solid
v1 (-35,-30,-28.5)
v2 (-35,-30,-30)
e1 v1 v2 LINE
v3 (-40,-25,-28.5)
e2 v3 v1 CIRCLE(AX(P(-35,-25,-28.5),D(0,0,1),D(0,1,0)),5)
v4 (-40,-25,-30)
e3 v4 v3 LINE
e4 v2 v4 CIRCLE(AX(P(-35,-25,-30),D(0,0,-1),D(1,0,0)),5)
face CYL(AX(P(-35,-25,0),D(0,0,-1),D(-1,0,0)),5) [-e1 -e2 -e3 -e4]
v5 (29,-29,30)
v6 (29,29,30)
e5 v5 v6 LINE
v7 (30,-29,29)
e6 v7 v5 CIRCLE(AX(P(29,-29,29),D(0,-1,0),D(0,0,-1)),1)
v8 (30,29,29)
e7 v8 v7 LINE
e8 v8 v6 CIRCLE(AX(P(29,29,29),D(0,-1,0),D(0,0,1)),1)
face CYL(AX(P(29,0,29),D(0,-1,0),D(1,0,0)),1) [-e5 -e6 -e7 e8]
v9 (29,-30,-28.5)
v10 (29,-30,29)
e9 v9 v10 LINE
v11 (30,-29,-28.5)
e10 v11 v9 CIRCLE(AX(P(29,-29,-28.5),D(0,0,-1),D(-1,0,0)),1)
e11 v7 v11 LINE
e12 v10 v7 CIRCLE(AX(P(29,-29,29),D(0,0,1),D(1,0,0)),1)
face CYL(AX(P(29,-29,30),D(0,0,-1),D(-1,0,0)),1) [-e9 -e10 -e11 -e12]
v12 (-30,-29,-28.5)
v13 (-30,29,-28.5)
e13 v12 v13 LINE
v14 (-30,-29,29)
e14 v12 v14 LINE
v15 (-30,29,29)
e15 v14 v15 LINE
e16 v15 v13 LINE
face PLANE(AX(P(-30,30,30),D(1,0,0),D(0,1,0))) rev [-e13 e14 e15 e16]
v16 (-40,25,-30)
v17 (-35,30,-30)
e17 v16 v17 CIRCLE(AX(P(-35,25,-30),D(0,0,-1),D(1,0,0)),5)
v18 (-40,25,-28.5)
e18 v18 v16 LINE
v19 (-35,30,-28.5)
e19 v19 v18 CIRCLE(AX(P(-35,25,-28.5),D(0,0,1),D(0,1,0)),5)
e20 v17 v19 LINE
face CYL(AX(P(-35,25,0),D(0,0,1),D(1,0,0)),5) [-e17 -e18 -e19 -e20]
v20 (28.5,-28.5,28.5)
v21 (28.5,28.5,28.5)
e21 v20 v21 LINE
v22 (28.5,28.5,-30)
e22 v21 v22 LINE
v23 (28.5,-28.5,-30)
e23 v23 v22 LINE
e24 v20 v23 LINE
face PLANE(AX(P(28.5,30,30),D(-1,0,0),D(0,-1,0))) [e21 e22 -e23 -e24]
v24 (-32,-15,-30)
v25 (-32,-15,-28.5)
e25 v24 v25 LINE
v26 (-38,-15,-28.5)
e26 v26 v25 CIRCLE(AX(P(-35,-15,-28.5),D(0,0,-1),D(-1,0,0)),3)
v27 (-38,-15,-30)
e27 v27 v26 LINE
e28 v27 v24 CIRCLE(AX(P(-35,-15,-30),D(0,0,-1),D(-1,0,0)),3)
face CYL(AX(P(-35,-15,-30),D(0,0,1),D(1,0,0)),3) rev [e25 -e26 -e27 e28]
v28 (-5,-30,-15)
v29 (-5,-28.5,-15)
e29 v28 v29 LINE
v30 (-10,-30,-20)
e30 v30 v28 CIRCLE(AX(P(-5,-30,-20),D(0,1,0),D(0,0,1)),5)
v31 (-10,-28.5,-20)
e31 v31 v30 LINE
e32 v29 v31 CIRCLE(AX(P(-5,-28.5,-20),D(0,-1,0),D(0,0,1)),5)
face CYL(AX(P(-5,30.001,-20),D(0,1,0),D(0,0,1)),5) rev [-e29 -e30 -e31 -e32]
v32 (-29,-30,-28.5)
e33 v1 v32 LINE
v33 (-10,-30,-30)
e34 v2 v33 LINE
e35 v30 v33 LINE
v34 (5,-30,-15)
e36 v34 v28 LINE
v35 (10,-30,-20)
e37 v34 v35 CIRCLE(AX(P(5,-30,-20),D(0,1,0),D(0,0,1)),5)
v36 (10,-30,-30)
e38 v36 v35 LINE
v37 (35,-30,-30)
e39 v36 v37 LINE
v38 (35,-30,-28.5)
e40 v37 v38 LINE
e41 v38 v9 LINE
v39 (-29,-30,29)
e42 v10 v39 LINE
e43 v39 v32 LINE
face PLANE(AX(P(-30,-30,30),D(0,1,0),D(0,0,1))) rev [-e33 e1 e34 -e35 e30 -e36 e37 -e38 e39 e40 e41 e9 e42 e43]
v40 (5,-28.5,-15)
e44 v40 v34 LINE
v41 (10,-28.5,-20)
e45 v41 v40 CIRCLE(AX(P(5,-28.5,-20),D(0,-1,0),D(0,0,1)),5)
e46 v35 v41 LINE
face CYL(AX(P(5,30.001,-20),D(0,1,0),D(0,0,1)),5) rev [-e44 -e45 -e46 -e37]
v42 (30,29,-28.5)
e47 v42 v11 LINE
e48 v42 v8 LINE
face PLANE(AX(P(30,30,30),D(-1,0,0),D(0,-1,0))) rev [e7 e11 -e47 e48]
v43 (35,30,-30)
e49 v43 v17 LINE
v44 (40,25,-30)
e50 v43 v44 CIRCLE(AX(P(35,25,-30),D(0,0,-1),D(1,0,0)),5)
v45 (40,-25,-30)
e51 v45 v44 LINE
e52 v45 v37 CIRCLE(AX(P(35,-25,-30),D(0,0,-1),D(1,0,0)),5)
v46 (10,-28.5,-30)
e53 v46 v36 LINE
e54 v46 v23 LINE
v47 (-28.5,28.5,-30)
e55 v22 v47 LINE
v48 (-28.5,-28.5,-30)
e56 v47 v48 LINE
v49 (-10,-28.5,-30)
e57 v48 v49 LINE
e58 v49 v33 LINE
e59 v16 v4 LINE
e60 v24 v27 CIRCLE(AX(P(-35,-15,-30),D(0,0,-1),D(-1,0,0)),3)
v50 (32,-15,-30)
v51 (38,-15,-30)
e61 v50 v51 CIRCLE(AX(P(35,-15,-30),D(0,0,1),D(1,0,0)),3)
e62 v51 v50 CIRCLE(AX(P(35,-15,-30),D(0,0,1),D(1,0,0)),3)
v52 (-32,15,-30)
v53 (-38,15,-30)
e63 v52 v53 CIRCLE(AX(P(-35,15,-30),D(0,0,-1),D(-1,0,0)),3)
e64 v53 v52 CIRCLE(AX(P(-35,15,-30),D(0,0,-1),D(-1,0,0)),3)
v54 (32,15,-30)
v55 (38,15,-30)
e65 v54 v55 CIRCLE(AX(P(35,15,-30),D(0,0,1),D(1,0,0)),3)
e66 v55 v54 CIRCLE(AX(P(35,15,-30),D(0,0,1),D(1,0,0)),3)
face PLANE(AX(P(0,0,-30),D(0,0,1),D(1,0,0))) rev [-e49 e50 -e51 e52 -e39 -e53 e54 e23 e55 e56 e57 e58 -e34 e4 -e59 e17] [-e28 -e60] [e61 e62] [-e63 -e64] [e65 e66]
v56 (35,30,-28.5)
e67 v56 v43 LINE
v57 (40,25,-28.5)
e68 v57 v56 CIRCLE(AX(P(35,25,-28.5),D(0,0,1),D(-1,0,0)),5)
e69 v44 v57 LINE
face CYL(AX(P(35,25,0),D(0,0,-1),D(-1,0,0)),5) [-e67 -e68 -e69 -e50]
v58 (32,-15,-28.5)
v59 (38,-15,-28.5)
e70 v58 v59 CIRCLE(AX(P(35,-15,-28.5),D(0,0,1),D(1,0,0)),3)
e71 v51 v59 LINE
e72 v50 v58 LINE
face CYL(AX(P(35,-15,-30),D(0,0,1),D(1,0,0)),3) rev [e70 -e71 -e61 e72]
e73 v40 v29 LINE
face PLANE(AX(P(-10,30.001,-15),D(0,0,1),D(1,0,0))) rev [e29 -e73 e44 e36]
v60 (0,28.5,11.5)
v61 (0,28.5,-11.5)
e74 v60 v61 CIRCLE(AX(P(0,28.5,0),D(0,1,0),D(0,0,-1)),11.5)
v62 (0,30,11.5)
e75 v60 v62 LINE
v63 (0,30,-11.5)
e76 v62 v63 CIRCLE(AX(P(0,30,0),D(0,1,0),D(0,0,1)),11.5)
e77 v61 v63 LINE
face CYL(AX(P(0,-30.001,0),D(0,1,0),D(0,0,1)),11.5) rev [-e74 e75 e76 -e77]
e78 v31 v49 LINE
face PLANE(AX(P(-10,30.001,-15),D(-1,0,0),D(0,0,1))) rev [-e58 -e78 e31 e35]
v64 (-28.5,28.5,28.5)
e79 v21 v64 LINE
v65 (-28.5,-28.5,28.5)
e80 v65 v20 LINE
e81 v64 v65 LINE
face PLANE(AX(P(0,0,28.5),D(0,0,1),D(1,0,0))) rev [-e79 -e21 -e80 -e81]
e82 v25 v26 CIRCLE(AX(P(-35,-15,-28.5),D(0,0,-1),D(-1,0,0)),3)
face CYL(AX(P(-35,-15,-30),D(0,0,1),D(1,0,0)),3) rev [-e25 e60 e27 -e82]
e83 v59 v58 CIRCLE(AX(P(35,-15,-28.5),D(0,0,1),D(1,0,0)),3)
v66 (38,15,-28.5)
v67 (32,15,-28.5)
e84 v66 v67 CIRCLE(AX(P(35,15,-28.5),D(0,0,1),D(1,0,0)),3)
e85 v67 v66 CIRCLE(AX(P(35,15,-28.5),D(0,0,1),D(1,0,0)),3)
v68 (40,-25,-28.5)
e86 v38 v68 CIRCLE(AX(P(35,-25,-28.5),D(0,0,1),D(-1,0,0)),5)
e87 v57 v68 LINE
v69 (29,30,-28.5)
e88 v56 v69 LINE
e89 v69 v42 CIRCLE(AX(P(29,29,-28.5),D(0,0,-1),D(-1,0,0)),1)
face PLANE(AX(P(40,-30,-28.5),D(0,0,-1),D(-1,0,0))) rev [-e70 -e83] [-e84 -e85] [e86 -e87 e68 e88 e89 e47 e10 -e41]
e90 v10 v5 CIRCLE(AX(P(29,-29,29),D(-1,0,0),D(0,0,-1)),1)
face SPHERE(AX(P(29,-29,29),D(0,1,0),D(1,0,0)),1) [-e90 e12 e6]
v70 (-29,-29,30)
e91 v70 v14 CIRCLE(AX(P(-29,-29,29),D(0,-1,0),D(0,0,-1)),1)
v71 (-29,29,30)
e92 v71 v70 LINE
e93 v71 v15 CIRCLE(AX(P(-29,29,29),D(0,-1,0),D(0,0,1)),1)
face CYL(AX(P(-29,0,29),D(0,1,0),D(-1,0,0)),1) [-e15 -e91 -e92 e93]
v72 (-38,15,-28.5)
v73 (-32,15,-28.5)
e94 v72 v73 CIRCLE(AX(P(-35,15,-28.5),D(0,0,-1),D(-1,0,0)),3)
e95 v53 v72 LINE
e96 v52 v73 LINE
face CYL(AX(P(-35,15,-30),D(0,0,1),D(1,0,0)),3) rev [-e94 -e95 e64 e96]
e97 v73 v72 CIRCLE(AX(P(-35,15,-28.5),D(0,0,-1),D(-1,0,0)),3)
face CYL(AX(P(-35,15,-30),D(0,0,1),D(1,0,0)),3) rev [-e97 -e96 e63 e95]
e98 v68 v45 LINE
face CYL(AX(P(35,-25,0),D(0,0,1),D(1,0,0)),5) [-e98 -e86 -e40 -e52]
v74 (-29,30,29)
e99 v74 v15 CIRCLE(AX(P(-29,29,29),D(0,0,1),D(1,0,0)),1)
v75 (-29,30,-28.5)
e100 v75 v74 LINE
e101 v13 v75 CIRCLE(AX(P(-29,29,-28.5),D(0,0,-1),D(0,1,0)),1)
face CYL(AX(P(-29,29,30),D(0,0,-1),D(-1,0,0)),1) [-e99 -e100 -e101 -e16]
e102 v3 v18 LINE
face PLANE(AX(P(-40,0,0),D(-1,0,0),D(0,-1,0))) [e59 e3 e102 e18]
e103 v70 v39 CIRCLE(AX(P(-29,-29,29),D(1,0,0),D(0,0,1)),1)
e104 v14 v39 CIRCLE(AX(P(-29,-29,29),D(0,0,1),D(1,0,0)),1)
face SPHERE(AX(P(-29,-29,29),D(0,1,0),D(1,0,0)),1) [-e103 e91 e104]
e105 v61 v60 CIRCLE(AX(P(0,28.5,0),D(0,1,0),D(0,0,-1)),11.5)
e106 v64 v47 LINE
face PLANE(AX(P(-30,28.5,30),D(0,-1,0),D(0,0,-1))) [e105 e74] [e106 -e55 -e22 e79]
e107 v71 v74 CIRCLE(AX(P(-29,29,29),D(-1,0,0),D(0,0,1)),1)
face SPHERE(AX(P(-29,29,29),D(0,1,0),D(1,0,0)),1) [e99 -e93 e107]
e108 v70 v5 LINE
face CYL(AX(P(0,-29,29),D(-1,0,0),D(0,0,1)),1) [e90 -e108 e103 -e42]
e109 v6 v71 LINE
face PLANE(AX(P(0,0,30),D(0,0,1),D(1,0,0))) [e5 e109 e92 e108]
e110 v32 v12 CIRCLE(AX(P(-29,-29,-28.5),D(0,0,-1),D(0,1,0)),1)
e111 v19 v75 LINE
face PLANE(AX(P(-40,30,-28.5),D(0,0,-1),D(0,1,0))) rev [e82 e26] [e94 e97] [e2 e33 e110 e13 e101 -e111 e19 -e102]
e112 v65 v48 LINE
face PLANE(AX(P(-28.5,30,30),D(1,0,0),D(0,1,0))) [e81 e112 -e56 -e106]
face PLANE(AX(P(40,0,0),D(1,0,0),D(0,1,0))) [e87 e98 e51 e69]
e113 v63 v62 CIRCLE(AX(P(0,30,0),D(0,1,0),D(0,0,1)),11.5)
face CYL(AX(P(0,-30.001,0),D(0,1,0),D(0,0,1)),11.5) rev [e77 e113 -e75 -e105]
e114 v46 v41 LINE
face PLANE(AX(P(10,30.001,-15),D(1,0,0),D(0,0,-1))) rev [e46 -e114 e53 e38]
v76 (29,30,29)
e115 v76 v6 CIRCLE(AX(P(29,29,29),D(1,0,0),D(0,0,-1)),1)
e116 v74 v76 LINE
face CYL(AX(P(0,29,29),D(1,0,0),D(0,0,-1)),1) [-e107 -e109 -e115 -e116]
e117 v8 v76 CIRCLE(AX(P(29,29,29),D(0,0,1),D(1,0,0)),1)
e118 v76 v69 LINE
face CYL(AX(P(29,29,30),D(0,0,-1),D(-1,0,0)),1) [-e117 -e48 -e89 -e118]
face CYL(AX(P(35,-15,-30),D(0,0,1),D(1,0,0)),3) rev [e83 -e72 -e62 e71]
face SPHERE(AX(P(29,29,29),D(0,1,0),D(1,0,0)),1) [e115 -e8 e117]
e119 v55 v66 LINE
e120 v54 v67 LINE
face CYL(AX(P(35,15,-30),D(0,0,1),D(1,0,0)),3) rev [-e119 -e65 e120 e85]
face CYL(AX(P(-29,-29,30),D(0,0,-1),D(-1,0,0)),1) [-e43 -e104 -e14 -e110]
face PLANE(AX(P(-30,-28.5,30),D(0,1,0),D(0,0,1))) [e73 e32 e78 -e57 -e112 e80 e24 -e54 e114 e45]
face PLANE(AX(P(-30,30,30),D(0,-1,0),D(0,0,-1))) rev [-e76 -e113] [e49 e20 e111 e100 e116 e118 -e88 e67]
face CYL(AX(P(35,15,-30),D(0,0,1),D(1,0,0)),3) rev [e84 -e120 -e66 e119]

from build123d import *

# Parameters (mm, degrees)
SKETCH_1_W          = 60
SKETCH_1_H          = 60
EXTRUDE_1_DEPTH     = 30
SHELL_1_T           = -1.5
SKETCH_5_W          = 1.5
SKETCH_5_H          = 60
EXTRUDE_3_DEPTH     = 10
SKETCH_6_W          = 1.5
SKETCH_6_H          = 60
EXTRUDE_4_DEPTH     = 10
CUT_EXTRUDE_3_REACH = 80.102
SKETCH_7_W          = 20
SKETCH_7_H          = 15
FILLET_1_R          = 5
FILLET_2_R          = 5
CUT_EXTRUDE_4_REACH = 80.102
SKETCH_8_R          = 11.5
FILLET_3_R          = 1
SKETCH_9_R          = 3
CUT_EXTRUDE_5_DEPTH = 77.956156349


with BuildPart() as part:
    # 草图1 → 凸台-拉伸1 (new, symmetric)
    with BuildSketch(Plane.XY):
        Rectangle(SKETCH_1_W, SKETCH_1_H)
    extrude(amount=EXTRUDE_1_DEPTH, both=True)

    # 抽壳1
    shell_1_openings = [part.faces().sort_by_distance(p)[0] for p in [
        (0, 0, -30),
    ]]
    offset(amount=SHELL_1_T, openings=shell_1_openings, kind=Kind.INTERSECTION)

    # 草图5 → 凸台-拉伸3 (add)
    with BuildSketch(Plane(origin=(30, 0, 0), x_dir=(0, 0, -1), z_dir=(1, 0, 0))):
        with Locations((29.25, 0)):
            Rectangle(SKETCH_5_W, SKETCH_5_H)
    extrude(amount=EXTRUDE_3_DEPTH)

    # 草图6 → 凸台-拉伸4 (add)
    with BuildSketch(Plane.ZY.offset(30)):
        with Locations((-29.25, 0)):
            Rectangle(SKETCH_6_W, SKETCH_6_H)
    extrude(amount=EXTRUDE_4_DEPTH)

    # 草图7 → 切除-拉伸3 (cut, up to next)
    with BuildSketch(Plane.XZ.offset(30), mode=Mode.PRIVATE) as cut_extrude_3_sk1:
        with Locations((0, -22.5)):
            Rectangle(SKETCH_7_W, SKETCH_7_H)
    cut_extrude_3_tool1 = extrude(cut_extrude_3_sk1.sketch, amount=-CUT_EXTRUDE_3_REACH, mode=Mode.PRIVATE) & part.part
    add(cut_extrude_3_tool1.solids().sort_by_distance((0, -30, -22.5))[0], mode=Mode.SUBTRACT)

    # 圆角1
    fillet_1_edges = [part.edges().sort_by_distance(p)[0] for p in [
        (10, -29.25, -15),
        (-10, -29.25, -15),
    ]]
    fillet(fillet_1_edges, radius=FILLET_1_R)

    # 圆角2
    fillet_2_edges = [part.edges().sort_by_distance(p)[0] for p in [
        (40, 30, -29.25),
        (40, -30, -29.25),
        (-40, -30, -29.25),
        (-40, 30, -29.25),
    ]]
    fillet(fillet_2_edges, radius=FILLET_2_R)

    # 草图8 → 切除-拉伸4 (cut, up to next)
    with BuildSketch(Plane(origin=(0, 30, 0), x_dir=(1, 0, 0), z_dir=(0, 1, 0)), mode=Mode.PRIVATE) as cut_extrude_4_sk1:
        with Locations(Location((0, 0, 0), (0, 0, 270))):
            Circle(SKETCH_8_R)
    cut_extrude_4_tool1 = extrude(cut_extrude_4_sk1.sketch, amount=-CUT_EXTRUDE_4_REACH, mode=Mode.PRIVATE) & part.part
    add(cut_extrude_4_tool1.solids().sort_by_distance((0, 30, 0))[0], mode=Mode.SUBTRACT)

    # 圆角3
    fillet_3_edges = [part.edges().sort_by_distance(p)[0] for p in [
        (-30, 0, 30),
        (0, -30, 30),
        (30, 0, 30),
        (0, 30, 30),
        (30, -30, 0.75),
        (-30, -30, 0.75),
        (-30, 30, 0.75),
        (30, 30, 0.75),
    ]]
    fillet(fillet_3_edges, radius=FILLET_3_R)

    # 草图9 → 切除-拉伸5 (cut, through all)
    with BuildSketch(Plane.XY.offset(-28.5)):
        with Locations((35, -15)):
            Circle(SKETCH_9_R)
        with Locations((35, 15)):
            Circle(SKETCH_9_R)
    cut_extrude_5 = extrude(amount=-CUT_EXTRUDE_5_DEPTH, mode=Mode.SUBTRACT)

    # 镜向1: 切除-拉伸5 across plane
    add(cut_extrude_5.mirror(Plane(origin=(0, 0, 0), x_dir=(0, 0, 1), z_dir=(1, 0, 0))), mode=Mode.SUBTRACT)


solid = part.part
